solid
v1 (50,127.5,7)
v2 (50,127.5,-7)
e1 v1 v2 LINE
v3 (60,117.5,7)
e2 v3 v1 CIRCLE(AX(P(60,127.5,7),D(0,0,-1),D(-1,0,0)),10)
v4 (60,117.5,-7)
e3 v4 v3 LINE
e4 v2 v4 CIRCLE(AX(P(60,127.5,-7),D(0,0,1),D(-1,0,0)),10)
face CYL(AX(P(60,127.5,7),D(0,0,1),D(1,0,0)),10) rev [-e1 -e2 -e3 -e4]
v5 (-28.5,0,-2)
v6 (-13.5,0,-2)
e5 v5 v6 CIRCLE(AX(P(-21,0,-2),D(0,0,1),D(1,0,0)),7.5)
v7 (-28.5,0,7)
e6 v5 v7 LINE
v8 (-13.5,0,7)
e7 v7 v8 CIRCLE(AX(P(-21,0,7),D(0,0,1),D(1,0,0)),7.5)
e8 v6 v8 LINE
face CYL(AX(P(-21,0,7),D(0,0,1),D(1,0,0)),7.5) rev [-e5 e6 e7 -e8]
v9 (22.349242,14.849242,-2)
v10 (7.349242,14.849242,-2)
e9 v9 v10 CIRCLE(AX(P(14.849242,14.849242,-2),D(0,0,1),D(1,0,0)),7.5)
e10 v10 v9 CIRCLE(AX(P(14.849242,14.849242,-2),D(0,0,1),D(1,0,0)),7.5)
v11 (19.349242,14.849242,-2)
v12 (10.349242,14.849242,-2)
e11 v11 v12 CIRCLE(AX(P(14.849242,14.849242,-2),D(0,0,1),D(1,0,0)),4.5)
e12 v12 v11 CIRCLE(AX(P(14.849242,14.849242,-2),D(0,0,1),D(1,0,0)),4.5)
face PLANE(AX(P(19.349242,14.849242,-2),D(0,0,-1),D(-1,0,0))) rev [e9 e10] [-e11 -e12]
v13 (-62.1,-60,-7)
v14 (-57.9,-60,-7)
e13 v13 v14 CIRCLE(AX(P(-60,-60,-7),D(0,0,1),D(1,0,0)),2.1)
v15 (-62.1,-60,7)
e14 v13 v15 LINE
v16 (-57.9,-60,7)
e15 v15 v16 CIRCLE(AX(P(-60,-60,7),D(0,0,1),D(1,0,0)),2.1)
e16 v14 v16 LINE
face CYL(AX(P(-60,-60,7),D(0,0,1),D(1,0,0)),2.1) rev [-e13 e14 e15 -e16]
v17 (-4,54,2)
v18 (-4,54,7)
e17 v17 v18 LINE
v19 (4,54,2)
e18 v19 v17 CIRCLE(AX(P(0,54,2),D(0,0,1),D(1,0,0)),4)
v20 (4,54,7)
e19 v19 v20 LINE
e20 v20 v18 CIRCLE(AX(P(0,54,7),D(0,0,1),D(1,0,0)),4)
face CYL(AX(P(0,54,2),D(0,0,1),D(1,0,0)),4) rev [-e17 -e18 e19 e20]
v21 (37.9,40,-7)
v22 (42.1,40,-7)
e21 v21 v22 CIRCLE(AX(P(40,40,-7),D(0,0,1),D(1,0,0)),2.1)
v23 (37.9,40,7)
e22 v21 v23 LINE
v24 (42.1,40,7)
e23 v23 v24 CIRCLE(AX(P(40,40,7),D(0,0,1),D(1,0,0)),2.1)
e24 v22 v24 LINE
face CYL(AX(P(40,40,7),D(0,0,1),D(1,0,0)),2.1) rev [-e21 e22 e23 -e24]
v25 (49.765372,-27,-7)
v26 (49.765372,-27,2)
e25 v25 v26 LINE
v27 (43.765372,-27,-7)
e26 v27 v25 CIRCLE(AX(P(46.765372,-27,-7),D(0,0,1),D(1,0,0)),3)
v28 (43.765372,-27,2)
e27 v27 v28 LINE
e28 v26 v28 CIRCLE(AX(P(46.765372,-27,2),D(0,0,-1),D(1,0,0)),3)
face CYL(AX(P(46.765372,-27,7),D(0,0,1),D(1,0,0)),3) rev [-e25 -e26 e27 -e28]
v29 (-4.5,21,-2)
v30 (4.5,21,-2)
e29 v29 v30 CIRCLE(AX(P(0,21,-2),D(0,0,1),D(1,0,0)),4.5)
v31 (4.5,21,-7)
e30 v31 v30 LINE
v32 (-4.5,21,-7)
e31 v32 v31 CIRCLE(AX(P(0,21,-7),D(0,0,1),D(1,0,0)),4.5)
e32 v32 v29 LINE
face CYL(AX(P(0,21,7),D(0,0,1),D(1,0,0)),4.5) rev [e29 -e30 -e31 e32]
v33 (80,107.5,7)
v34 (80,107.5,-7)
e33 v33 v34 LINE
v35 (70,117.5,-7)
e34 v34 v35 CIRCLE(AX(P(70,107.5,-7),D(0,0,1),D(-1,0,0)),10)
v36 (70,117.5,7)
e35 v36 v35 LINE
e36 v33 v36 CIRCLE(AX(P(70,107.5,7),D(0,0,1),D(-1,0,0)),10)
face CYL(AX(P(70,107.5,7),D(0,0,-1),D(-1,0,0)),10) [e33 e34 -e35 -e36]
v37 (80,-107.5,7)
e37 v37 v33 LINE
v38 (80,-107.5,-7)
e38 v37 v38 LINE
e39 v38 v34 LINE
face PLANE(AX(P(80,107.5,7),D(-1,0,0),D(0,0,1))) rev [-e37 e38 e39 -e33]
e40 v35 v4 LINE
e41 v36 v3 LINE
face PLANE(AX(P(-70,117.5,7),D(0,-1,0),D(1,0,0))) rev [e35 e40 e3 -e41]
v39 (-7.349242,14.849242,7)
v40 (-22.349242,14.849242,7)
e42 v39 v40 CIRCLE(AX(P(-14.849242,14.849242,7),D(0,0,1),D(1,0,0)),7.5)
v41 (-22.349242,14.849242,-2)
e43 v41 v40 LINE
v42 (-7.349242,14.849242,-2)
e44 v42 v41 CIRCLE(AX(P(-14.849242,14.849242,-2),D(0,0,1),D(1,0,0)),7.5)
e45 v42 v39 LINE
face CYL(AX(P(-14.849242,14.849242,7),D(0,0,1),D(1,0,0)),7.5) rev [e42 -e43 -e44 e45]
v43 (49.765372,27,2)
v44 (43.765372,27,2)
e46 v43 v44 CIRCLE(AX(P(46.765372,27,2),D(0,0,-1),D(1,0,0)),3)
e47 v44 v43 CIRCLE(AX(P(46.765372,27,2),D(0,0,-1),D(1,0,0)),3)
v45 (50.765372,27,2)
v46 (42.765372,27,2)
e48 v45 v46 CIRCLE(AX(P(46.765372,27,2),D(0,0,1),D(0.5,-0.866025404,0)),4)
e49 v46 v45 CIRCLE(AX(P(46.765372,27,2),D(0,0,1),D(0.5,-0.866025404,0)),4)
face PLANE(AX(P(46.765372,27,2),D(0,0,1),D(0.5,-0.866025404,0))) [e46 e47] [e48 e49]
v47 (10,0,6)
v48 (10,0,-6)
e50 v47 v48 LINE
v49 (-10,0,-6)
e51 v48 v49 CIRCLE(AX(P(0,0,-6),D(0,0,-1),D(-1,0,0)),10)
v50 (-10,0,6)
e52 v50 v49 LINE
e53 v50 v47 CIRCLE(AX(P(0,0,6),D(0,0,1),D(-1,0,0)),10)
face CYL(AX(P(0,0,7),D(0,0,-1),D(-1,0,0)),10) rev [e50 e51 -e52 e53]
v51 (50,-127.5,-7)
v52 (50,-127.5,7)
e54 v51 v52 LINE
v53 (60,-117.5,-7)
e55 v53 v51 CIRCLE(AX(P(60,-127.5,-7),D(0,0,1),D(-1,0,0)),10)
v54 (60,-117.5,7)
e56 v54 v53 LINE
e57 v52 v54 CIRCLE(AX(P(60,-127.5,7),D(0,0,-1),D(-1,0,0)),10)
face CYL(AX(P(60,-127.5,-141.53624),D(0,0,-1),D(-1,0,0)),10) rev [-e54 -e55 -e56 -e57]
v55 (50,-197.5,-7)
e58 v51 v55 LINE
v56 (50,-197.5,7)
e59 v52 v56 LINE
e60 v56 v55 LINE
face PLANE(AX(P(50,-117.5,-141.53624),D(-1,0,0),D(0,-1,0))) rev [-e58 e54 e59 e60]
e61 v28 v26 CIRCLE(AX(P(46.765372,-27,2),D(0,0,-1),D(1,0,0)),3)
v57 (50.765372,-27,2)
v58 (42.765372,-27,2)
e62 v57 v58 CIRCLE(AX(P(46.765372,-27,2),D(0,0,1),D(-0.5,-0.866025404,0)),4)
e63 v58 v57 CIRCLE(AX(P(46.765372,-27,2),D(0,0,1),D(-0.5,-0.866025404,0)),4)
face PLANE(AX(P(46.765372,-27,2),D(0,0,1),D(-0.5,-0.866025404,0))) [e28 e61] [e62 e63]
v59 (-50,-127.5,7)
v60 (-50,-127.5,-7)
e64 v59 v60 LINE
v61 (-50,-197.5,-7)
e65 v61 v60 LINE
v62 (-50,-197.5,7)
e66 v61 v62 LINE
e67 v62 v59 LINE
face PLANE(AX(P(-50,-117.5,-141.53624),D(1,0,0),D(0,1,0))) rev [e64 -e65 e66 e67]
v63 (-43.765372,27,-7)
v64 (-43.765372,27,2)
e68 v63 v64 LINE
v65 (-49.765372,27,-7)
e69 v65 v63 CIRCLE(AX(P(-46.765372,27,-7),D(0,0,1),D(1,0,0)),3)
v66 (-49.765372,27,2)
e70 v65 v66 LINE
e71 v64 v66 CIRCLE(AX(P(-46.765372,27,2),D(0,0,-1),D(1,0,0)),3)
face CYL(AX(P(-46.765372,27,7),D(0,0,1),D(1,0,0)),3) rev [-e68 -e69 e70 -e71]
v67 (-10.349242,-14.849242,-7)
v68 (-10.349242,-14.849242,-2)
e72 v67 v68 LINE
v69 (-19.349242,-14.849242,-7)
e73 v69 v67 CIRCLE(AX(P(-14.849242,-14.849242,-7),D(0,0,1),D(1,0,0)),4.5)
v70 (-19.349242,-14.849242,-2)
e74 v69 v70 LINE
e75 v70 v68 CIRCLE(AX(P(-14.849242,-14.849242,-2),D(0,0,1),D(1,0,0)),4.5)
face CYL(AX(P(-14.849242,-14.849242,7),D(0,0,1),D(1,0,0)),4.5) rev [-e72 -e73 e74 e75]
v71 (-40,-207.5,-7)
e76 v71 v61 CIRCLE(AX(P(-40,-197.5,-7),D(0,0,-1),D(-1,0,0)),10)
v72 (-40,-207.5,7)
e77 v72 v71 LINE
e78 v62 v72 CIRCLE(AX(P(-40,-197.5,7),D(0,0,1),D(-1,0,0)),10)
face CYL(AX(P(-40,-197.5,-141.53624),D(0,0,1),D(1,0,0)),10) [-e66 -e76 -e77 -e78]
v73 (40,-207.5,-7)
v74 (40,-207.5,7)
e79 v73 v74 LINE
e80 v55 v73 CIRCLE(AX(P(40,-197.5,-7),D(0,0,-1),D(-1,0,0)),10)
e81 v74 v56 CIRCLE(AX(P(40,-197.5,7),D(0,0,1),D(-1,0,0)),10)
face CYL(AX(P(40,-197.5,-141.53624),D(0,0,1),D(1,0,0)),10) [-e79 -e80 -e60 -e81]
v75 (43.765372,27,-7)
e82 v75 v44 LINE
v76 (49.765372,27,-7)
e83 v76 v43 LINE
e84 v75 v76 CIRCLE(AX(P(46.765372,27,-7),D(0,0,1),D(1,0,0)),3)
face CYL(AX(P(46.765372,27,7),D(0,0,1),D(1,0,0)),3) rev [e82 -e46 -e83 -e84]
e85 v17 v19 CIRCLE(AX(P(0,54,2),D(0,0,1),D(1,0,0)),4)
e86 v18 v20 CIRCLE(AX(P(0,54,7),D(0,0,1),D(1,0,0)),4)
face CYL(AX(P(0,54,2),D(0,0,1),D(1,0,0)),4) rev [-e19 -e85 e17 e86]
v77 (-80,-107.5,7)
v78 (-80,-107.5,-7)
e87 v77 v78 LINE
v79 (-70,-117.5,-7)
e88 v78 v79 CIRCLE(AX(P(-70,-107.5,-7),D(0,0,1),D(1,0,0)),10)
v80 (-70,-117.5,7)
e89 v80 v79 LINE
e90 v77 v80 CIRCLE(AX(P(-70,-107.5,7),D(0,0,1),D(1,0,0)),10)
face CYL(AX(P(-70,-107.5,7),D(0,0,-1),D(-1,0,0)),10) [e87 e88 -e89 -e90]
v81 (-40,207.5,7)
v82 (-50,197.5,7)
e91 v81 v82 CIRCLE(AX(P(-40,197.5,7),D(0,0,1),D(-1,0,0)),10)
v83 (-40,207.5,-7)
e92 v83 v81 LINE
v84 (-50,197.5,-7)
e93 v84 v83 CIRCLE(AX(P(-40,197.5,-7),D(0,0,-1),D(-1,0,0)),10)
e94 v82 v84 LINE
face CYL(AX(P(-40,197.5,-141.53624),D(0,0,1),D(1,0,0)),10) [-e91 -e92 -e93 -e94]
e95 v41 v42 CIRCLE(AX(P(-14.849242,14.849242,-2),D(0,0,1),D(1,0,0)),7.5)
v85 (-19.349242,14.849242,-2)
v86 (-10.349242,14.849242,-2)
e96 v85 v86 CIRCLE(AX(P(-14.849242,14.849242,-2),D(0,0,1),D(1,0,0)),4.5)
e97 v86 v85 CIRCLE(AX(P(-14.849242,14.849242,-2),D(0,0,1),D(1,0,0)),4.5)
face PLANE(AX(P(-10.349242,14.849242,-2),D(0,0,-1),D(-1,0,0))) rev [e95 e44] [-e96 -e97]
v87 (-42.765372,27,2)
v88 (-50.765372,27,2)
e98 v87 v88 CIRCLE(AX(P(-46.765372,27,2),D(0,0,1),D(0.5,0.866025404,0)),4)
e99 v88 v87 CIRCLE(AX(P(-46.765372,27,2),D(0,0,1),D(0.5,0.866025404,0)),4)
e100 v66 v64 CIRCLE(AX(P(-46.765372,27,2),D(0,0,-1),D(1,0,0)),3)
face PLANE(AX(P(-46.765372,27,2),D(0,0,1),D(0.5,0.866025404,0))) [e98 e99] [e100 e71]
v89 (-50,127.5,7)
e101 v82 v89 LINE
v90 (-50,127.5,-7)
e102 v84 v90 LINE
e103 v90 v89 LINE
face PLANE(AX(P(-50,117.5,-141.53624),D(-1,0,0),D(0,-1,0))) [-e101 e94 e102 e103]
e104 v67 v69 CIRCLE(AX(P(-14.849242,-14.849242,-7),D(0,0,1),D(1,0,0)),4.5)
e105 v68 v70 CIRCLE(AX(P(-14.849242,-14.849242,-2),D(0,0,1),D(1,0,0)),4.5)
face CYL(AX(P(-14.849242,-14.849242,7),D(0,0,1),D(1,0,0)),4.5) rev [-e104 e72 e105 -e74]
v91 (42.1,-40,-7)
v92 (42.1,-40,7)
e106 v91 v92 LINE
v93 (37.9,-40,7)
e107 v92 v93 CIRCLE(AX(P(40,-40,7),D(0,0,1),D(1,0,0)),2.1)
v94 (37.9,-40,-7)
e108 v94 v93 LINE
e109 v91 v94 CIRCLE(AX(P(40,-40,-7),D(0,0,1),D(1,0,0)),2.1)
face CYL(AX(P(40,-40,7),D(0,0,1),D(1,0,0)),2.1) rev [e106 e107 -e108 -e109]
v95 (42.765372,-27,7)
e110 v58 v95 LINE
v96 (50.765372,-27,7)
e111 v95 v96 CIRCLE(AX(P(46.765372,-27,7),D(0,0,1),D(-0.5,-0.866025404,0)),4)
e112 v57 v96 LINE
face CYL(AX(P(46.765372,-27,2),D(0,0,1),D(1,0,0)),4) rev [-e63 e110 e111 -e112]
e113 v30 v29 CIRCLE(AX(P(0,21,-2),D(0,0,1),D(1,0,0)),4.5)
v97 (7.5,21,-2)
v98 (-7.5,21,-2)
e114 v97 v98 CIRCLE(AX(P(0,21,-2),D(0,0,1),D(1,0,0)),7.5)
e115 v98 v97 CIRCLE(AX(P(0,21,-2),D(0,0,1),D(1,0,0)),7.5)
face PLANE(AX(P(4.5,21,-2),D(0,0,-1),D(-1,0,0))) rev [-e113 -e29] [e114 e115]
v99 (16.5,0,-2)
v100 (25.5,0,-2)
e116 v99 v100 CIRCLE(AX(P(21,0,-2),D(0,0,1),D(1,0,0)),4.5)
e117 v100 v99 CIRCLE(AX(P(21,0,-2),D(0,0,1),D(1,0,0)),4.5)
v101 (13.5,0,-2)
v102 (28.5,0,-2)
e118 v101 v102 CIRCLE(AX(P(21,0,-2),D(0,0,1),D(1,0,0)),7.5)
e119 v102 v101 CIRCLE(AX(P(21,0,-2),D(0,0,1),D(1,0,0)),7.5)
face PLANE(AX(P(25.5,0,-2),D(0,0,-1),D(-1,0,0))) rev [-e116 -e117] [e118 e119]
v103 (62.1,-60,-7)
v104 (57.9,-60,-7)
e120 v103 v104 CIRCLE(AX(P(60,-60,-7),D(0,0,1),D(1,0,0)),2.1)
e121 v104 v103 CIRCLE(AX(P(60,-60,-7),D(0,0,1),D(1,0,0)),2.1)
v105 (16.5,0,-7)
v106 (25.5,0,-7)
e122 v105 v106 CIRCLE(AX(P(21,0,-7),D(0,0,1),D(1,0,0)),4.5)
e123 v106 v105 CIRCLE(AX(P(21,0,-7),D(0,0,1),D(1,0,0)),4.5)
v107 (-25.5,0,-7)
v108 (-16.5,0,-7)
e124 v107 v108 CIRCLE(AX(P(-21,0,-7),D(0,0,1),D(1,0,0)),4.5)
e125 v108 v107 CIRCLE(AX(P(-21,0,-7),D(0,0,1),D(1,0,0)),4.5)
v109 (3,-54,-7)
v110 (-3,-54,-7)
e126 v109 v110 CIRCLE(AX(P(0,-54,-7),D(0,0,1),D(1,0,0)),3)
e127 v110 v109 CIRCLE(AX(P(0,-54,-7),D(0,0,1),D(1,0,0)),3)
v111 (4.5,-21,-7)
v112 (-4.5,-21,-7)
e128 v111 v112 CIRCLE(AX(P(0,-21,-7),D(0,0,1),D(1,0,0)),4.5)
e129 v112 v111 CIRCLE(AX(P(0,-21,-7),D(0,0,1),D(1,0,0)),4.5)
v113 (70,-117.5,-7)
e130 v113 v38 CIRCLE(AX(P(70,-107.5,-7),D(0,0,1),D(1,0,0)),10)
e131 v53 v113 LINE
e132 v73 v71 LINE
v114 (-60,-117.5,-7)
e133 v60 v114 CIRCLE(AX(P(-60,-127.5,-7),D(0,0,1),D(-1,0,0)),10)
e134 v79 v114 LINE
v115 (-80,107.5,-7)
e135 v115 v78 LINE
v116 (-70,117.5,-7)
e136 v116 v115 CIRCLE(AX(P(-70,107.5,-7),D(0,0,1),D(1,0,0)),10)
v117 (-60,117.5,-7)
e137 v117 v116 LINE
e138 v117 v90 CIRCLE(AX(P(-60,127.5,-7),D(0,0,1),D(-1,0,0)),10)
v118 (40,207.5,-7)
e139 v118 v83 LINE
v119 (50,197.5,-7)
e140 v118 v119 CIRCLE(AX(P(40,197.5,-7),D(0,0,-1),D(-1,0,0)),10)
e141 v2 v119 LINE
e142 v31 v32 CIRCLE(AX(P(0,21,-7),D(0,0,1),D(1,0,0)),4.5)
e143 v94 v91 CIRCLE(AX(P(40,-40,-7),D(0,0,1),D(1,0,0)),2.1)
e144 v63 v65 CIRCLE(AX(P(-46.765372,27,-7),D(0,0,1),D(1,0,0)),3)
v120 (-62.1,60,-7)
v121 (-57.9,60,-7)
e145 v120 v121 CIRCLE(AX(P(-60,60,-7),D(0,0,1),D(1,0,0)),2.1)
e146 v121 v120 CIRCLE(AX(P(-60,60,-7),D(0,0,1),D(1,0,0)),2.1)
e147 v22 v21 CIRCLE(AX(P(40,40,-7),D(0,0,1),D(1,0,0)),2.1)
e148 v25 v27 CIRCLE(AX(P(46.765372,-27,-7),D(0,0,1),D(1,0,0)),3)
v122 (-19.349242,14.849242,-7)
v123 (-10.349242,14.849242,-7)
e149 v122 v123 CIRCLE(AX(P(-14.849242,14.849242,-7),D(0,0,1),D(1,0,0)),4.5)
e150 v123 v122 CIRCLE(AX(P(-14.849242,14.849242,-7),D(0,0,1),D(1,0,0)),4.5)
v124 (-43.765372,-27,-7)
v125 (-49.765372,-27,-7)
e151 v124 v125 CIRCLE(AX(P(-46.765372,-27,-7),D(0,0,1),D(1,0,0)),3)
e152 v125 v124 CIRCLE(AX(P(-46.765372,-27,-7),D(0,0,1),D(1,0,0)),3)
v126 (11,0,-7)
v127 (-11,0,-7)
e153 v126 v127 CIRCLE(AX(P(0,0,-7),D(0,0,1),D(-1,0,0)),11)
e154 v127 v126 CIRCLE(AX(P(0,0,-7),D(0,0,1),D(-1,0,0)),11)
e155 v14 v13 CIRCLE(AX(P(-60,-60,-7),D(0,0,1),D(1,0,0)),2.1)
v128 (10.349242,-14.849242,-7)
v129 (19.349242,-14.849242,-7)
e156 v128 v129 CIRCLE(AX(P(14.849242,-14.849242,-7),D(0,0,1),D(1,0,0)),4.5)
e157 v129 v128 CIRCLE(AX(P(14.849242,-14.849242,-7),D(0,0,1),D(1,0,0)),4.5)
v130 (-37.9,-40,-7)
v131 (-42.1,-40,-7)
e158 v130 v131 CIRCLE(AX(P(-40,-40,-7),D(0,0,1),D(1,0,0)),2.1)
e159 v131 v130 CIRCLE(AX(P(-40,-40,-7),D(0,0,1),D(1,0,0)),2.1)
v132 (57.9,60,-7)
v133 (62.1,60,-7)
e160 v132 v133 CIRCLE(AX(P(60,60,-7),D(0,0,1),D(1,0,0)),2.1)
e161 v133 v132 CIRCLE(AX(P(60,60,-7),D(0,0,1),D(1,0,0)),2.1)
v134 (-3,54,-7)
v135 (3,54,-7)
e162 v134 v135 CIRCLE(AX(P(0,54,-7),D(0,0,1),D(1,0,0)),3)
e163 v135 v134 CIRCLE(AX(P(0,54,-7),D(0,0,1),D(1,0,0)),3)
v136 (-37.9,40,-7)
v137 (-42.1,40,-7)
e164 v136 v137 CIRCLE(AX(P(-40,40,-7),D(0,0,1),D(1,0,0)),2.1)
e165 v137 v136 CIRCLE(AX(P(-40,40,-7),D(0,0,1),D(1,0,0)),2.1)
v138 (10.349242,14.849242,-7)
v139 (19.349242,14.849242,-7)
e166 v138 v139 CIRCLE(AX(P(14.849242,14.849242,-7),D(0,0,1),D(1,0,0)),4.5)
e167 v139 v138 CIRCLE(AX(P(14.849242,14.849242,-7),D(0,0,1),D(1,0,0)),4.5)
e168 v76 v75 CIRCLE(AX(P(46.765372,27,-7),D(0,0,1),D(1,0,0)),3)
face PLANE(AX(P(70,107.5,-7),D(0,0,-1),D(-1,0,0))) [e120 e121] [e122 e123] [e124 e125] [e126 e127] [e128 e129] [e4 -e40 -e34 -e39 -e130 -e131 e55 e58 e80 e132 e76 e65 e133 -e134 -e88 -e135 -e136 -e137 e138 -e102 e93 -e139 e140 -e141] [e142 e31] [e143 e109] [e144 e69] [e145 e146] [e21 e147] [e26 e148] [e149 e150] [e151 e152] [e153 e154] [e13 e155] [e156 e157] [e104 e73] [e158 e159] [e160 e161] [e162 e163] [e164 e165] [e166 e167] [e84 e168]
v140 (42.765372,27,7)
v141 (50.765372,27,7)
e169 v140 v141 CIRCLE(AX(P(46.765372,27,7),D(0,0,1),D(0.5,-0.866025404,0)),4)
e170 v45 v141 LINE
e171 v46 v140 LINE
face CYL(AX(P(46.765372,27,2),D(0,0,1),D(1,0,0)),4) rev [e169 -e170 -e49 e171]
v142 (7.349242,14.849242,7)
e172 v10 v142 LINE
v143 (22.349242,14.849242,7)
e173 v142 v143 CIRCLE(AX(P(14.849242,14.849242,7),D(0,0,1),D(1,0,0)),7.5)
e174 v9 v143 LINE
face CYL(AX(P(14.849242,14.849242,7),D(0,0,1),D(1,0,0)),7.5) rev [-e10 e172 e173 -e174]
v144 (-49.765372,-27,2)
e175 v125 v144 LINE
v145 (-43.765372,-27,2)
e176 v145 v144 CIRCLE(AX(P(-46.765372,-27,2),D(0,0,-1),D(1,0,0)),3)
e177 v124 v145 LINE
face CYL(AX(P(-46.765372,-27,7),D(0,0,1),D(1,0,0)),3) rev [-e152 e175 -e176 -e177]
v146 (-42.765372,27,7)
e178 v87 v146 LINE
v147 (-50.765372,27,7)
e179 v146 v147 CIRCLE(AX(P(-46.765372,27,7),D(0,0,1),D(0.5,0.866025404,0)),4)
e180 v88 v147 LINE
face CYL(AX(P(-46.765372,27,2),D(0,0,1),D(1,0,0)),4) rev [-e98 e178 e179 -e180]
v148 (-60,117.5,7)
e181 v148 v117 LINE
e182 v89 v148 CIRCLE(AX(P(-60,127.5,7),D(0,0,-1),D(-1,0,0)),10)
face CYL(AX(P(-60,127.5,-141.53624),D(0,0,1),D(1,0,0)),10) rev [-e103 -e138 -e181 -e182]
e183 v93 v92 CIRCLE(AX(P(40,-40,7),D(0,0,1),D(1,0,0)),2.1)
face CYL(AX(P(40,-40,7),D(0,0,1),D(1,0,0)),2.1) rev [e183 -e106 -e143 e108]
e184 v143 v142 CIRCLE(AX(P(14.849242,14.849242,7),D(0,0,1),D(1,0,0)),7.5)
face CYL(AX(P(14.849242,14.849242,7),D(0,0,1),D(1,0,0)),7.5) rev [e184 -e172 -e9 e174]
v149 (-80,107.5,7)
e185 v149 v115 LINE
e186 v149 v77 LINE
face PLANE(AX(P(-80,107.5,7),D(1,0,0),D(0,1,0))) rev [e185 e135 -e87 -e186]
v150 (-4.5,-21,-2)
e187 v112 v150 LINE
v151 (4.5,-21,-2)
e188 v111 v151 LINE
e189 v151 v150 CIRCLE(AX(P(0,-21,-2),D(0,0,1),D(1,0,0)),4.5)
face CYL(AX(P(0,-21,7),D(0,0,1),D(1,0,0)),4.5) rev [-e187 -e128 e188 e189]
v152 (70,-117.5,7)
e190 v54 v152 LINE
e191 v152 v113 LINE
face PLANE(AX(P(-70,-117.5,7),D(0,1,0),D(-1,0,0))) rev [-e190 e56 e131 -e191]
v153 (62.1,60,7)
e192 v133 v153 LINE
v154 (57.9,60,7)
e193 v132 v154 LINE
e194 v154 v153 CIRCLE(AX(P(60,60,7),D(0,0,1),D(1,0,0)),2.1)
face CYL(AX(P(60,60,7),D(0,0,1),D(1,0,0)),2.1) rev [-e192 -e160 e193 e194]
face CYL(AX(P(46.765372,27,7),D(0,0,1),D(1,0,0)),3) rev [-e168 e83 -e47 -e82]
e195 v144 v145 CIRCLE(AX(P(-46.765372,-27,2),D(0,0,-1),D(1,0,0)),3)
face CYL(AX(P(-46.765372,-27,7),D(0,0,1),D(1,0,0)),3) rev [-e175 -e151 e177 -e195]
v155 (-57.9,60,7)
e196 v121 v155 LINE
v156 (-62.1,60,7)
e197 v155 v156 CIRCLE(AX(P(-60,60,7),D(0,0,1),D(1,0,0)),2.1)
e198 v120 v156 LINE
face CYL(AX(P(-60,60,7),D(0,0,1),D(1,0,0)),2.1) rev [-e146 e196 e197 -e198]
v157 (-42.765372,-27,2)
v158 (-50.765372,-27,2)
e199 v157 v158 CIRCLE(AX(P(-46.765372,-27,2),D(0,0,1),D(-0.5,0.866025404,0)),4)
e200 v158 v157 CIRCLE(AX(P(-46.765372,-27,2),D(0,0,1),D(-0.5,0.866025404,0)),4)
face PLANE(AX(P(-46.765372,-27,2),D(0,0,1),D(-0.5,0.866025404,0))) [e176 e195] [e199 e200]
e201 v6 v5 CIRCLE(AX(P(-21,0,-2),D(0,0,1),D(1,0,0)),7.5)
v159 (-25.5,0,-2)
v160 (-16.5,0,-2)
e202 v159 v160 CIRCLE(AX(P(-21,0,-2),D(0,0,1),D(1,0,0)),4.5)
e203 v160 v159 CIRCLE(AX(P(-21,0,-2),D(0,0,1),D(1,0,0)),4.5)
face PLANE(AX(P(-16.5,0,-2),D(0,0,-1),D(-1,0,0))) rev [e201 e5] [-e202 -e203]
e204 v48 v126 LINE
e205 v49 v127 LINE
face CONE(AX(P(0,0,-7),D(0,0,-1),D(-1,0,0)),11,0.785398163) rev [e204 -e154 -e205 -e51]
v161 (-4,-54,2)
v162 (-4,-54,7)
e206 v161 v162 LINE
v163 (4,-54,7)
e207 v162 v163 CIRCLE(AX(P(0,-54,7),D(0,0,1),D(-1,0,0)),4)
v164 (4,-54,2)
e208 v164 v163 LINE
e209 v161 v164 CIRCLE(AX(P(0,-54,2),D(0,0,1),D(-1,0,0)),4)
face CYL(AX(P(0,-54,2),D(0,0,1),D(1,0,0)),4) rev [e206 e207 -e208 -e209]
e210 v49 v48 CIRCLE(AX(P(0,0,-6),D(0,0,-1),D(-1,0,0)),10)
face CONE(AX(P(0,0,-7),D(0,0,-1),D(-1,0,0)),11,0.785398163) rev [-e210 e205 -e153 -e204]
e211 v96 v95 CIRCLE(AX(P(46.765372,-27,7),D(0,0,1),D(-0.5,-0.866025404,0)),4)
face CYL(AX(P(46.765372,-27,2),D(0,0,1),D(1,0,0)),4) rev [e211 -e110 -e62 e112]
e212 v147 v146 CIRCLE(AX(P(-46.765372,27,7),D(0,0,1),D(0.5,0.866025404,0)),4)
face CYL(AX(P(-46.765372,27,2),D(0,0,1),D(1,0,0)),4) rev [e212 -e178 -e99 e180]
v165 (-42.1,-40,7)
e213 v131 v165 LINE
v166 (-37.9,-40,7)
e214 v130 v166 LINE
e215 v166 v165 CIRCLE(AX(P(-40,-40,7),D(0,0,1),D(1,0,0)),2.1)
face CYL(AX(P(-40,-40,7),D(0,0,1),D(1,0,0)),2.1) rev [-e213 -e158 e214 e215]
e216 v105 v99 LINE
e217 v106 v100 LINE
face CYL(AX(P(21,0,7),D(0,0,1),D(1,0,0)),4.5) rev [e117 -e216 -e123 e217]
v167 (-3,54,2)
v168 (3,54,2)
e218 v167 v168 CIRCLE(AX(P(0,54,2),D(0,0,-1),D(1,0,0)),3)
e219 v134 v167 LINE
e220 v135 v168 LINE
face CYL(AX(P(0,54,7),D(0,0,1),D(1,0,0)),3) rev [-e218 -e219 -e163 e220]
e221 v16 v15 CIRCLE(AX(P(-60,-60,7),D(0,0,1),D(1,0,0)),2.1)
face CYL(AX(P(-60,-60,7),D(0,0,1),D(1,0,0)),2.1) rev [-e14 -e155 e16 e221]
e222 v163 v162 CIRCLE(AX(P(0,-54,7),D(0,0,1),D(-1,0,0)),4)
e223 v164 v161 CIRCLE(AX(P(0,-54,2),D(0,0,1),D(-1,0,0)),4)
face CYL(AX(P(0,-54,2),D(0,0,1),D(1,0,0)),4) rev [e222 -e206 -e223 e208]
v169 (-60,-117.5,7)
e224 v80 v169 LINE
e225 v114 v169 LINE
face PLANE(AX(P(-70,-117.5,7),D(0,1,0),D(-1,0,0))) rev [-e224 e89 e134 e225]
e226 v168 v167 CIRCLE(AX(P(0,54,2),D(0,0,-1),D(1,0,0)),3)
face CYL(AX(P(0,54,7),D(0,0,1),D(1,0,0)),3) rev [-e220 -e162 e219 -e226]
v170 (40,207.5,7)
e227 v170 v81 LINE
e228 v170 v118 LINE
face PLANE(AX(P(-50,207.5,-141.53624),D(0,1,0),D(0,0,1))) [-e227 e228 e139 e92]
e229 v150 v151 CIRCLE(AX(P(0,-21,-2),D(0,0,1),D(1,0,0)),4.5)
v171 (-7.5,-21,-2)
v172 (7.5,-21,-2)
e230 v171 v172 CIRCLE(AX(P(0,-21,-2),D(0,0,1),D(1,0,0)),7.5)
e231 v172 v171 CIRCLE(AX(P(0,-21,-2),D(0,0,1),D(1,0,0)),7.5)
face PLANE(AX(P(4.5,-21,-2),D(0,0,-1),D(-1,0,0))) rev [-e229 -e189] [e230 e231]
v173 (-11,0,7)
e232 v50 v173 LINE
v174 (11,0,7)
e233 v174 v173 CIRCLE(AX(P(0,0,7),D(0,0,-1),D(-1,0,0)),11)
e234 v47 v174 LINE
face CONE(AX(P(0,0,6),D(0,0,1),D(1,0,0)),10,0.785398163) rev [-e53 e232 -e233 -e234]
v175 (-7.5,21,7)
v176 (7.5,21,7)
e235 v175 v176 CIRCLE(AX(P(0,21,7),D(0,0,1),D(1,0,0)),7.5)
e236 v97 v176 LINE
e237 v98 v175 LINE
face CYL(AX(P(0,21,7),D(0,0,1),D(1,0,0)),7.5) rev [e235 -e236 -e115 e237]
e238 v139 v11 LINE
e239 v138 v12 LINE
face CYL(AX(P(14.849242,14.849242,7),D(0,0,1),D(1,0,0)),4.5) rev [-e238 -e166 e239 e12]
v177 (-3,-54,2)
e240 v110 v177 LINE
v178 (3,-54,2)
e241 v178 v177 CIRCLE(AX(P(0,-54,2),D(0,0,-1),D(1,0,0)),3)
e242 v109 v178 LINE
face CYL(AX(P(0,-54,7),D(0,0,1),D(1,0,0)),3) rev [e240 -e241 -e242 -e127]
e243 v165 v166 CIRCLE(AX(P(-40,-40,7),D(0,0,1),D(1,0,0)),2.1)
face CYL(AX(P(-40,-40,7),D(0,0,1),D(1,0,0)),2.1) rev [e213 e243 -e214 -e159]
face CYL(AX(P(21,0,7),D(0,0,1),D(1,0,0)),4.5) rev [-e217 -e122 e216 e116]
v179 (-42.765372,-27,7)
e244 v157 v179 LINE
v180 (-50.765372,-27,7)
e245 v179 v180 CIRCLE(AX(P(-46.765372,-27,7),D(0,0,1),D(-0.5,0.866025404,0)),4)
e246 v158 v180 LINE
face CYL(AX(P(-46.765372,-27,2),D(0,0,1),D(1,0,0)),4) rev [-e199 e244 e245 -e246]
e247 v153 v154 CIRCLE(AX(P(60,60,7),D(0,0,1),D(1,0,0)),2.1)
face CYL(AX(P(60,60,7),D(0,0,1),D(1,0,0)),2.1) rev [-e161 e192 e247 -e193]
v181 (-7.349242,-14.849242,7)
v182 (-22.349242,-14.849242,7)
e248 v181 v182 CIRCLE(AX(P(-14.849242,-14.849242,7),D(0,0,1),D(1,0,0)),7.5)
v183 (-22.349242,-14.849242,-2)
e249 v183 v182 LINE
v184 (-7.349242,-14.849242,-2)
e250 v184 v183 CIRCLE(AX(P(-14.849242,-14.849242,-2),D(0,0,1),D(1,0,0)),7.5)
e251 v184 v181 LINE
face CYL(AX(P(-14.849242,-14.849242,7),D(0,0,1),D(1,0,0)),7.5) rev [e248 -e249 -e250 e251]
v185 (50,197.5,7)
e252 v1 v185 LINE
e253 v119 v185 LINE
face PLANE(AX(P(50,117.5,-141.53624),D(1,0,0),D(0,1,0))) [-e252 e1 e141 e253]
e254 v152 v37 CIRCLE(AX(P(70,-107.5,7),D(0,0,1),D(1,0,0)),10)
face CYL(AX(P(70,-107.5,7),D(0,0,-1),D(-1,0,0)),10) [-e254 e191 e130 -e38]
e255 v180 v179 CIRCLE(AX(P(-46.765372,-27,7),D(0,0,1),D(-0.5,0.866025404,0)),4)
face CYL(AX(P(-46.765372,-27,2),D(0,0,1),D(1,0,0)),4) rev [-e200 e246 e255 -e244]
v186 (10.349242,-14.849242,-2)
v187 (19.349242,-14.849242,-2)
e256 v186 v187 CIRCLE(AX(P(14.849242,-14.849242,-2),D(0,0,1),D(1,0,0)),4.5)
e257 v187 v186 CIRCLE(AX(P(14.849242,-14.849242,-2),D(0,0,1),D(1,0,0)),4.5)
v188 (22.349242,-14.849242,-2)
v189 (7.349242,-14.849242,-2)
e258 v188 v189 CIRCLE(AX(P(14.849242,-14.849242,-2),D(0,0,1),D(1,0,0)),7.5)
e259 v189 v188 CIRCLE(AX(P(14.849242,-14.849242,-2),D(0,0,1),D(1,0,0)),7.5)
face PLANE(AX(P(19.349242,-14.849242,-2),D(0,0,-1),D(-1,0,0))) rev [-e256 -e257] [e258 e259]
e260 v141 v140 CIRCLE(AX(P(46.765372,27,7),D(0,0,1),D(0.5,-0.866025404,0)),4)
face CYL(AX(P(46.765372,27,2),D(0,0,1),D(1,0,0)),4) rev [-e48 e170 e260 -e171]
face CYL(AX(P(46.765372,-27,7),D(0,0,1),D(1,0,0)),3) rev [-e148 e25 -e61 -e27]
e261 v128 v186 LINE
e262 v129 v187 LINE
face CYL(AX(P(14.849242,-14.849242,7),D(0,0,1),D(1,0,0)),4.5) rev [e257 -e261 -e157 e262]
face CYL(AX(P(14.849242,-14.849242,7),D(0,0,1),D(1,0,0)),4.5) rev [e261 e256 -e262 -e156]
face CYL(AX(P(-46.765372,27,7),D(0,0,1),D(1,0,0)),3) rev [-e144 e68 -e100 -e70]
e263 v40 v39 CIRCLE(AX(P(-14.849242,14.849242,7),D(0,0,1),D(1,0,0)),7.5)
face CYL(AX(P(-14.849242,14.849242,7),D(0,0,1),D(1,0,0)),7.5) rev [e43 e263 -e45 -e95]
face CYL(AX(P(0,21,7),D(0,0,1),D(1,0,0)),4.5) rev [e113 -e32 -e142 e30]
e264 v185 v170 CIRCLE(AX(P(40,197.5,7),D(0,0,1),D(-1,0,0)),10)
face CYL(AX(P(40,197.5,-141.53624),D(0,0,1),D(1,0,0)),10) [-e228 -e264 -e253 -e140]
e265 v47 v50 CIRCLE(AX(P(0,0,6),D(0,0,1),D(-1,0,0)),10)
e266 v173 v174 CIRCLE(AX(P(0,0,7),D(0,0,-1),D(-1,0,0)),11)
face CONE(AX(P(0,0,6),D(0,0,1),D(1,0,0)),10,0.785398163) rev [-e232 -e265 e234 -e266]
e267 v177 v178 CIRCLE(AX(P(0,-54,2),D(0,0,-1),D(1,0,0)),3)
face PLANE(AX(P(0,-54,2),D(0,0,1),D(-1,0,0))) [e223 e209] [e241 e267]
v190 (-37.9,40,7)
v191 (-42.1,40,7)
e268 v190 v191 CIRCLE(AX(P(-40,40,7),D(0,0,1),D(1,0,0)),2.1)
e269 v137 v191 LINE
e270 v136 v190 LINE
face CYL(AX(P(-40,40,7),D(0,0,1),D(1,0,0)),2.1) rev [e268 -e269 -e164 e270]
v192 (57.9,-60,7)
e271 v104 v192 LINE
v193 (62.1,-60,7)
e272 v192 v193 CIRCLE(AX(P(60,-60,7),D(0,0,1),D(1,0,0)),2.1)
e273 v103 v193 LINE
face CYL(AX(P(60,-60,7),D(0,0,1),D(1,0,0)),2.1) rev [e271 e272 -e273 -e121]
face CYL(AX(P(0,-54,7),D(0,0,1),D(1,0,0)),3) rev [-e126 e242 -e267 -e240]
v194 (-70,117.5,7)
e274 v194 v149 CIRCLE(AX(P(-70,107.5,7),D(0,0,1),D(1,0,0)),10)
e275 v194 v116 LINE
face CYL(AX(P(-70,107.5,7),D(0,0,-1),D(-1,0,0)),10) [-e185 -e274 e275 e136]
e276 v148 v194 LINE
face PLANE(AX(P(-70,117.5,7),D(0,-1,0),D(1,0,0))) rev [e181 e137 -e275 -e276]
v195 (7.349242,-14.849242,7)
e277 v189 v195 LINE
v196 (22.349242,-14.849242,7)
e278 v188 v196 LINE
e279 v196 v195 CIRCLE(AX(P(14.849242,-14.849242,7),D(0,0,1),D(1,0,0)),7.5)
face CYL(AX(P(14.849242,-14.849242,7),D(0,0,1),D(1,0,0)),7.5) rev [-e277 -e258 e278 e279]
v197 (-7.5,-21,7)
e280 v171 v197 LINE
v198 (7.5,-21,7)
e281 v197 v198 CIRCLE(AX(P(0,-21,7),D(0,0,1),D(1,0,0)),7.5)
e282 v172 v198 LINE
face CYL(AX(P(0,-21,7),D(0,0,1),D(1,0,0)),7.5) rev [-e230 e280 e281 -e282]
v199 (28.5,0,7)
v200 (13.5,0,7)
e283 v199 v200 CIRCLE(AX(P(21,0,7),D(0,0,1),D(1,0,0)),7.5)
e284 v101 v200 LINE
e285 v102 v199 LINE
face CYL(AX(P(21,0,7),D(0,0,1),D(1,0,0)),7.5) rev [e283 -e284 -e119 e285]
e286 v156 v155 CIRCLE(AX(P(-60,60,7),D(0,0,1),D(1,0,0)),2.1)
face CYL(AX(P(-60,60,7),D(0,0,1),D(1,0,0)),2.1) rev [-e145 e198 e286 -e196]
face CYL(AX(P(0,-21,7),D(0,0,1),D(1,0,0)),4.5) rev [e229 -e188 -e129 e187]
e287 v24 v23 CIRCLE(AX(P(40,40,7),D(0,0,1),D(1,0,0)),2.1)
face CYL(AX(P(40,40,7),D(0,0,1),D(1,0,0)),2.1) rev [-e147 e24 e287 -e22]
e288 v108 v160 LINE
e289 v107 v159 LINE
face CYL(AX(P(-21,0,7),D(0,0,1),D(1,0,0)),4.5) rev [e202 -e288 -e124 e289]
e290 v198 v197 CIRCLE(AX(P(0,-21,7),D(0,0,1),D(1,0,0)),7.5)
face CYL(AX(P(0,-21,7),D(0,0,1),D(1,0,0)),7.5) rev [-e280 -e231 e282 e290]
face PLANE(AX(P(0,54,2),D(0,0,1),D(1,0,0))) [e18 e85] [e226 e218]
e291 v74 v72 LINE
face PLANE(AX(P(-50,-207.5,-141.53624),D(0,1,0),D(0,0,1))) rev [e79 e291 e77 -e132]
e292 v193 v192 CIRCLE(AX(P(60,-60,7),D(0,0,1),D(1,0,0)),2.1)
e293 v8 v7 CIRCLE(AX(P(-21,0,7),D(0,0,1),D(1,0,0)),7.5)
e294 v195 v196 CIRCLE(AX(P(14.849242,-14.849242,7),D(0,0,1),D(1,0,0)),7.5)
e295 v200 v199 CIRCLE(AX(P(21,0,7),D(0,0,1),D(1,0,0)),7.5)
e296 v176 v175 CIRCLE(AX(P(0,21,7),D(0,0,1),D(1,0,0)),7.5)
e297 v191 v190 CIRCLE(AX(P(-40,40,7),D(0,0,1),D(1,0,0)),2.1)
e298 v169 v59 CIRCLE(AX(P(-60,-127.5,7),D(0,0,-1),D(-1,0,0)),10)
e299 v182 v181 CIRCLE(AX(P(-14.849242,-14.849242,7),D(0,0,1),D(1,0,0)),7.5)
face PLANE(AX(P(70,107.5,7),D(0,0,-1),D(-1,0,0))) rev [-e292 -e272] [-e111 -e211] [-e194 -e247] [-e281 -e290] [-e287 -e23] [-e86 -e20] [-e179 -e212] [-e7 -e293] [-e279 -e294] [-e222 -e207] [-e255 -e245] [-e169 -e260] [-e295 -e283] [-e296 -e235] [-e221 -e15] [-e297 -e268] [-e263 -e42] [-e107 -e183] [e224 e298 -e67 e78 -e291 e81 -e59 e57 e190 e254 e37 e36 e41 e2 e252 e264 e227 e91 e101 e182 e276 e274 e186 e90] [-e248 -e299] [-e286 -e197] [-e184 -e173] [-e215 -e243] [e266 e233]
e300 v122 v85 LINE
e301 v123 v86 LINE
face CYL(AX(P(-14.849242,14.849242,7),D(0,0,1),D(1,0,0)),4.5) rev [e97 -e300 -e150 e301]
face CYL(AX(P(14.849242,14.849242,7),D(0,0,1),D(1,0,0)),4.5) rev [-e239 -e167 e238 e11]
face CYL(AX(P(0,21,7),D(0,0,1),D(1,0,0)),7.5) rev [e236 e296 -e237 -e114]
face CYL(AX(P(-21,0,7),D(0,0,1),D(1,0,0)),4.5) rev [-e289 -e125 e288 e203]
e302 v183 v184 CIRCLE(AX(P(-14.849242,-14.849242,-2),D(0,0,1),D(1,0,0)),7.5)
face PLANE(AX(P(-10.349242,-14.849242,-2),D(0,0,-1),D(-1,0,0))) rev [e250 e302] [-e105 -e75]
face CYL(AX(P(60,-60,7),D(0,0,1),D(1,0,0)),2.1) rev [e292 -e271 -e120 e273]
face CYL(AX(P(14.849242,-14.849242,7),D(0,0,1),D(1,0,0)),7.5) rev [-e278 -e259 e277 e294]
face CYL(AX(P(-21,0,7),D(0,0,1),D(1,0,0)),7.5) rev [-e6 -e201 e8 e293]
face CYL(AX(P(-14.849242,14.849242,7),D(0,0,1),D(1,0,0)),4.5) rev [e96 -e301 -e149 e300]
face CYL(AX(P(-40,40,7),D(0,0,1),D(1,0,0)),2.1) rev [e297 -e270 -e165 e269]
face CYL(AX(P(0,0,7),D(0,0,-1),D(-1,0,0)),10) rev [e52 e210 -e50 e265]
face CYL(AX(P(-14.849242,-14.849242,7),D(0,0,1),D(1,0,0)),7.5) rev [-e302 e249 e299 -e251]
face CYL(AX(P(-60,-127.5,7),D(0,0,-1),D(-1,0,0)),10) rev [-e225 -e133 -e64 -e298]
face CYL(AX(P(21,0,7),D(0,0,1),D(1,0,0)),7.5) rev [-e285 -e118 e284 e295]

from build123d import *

# Parameters (mm, degrees)
SKETCH_1_R                = 10
EXTRUDE_1_DEPTH           = 7
HOLE_WIZARD_3_D           = 9
HOLE_WIZARD_3_CBORE_D     = 15
HOLE_WIZARD_3_CBORE_DEPTH = 9
PATTERN_CIRCULAR_1_COUNT  = 8
CHAMFER_1_SIZE            = 1
HOLE_WIZARD_6_0_6_1_D     = 6
SKETCH_14_R               = 4
CUT_EXTRUDE_1_DEPTH       = 5
HOLE_WIZARD_M5_1_D        = 4.2
PATTERN_CIRCULAR_2_COUNT  = 6
SKETCH_15_W               = 100
SKETCH_15_H               = 90
EXTRUDE_2_DEPTH           = 14
FILLET_1_R                = 10


with BuildPart() as part:
    # 草图1 → 凸台-拉伸1 (new, symmetric)
    with BuildSketch(Plane.XY):
        with BuildLine():
            Line((-70, 117.5), (70, 117.5))
            ThreePointArc((70, 117.5), (77.071067812, 114.571067812), (80, 107.5))
            Line((80, 107.5), (80, -107.5))
            ThreePointArc((80, -107.5), (77.071067812, -114.571067812), (70, -117.5))
            Line((70, -117.5), (-70, -117.5))
            ThreePointArc((-70, -117.5), (-77.071067812, -114.571067812), (-80, -107.5))
            Line((-80, -107.5), (-80, 107.5))
            ThreePointArc((-80, 107.5), (-77.071067812, 114.571067812), (-70, 117.5))
        make_face()
        Circle(SKETCH_1_R, mode=Mode.SUBTRACT)
    extrude(amount=EXTRUDE_1_DEPTH, both=True)

    # 打孔尺寸(%根据)内六角圆柱头螺钉的类型3 (through all)
    with Locations(Plane.XY.offset(7)):
        with Locations((0, 21)):
            hole_wizard_3 = CounterBoreHole(HOLE_WIZARD_3_D / 2, HOLE_WIZARD_3_CBORE_D / 2, HOLE_WIZARD_3_CBORE_DEPTH)

    # 阵列(圆周)1: 打孔尺寸(%根据)内六角圆柱头螺钉的类型3 ×8 about axis
    pattern_circular_1_axis = Axis((0, 0, 0), (0, 0, 1))
    for i in range(1, PATTERN_CIRCULAR_1_COUNT):
        add(hole_wizard_3.rotate(pattern_circular_1_axis, i * 360 / PATTERN_CIRCULAR_1_COUNT), mode=Mode.SUBTRACT)

    # 倒角1
    chamfer_1_edges = [part.edges().sort_by_distance(p)[0] for p in [
        (-10, 0, -7),
        (-10, 0, 7),
    ]]
    chamfer(chamfer_1_edges, length=CHAMFER_1_SIZE)

    # Ø6.0 (6) 直径孔1 (through all)
    with Locations(Plane.XY.offset(7)):
        with Locations((0, 54)):
            hole_wizard_6_0_6_1 = Hole(HOLE_WIZARD_6_0_6_1_D / 2)

    # 草图14 → 切除-拉伸1 (cut)
    with BuildSketch(Plane.XY.offset(7)):
        with Locations((0, 54)):
            Circle(SKETCH_14_R)
    cut_extrude_1 = extrude(amount=-CUT_EXTRUDE_1_DEPTH, mode=Mode.SUBTRACT)

    # M5 螺纹孔1 (through all)
    with Locations(Plane.XY.offset(7)):
        with Locations((-60, 60), (-40, 40), (40, 40), (40, -40), (-40, -40), (-60, -60), (60, -60), (60, 60)):
            Hole(HOLE_WIZARD_M5_1_D / 2)

    # 阵列(圆周)2: Ø6.0 (6) 直径孔1, 切除-拉伸1 ×6 about axis
    pattern_circular_2_axis = Axis((0, 0, 0), (0, 0, 1))
    add([hole_wizard_6_0_6_1.rotate(pattern_circular_2_axis, i * 360 / PATTERN_CIRCULAR_2_COUNT) for i in range(1, PATTERN_CIRCULAR_2_COUNT)], mode=Mode.SUBTRACT)
    add([cut_extrude_1.rotate(pattern_circular_2_axis, i * 360 / PATTERN_CIRCULAR_2_COUNT) for i in range(1, PATTERN_CIRCULAR_2_COUNT)], mode=Mode.SUBTRACT)

    # 草图15 → 凸台-拉伸2 (add)
    with BuildSketch(Plane.XY.offset(7)):
        with Locations((0, 162.5)):
            Rectangle(SKETCH_15_W, SKETCH_15_H)
    extrude_2 = extrude(amount=-EXTRUDE_2_DEPTH)

    # 镜向1: 凸台-拉伸2 across plane
    add(extrude_2.mirror(Plane.ZX))

    # 圆角1
    fillet_1_edges = [part.edges().sort_by_distance(p)[0] for p in [
        (50, 117.5, 0),
        (50, 207.5, 0),
        (-50, 207.5, 0),
        (-50, 117.5, 0),
        (-50, -207.5, 0),
        (-50, -117.5, 0),
        (50, -117.5, 0),
        (50, -207.5, 0),
    ]]
    fillet(fillet_1_edges, radius=FILLET_1_R)


solid = part.part
